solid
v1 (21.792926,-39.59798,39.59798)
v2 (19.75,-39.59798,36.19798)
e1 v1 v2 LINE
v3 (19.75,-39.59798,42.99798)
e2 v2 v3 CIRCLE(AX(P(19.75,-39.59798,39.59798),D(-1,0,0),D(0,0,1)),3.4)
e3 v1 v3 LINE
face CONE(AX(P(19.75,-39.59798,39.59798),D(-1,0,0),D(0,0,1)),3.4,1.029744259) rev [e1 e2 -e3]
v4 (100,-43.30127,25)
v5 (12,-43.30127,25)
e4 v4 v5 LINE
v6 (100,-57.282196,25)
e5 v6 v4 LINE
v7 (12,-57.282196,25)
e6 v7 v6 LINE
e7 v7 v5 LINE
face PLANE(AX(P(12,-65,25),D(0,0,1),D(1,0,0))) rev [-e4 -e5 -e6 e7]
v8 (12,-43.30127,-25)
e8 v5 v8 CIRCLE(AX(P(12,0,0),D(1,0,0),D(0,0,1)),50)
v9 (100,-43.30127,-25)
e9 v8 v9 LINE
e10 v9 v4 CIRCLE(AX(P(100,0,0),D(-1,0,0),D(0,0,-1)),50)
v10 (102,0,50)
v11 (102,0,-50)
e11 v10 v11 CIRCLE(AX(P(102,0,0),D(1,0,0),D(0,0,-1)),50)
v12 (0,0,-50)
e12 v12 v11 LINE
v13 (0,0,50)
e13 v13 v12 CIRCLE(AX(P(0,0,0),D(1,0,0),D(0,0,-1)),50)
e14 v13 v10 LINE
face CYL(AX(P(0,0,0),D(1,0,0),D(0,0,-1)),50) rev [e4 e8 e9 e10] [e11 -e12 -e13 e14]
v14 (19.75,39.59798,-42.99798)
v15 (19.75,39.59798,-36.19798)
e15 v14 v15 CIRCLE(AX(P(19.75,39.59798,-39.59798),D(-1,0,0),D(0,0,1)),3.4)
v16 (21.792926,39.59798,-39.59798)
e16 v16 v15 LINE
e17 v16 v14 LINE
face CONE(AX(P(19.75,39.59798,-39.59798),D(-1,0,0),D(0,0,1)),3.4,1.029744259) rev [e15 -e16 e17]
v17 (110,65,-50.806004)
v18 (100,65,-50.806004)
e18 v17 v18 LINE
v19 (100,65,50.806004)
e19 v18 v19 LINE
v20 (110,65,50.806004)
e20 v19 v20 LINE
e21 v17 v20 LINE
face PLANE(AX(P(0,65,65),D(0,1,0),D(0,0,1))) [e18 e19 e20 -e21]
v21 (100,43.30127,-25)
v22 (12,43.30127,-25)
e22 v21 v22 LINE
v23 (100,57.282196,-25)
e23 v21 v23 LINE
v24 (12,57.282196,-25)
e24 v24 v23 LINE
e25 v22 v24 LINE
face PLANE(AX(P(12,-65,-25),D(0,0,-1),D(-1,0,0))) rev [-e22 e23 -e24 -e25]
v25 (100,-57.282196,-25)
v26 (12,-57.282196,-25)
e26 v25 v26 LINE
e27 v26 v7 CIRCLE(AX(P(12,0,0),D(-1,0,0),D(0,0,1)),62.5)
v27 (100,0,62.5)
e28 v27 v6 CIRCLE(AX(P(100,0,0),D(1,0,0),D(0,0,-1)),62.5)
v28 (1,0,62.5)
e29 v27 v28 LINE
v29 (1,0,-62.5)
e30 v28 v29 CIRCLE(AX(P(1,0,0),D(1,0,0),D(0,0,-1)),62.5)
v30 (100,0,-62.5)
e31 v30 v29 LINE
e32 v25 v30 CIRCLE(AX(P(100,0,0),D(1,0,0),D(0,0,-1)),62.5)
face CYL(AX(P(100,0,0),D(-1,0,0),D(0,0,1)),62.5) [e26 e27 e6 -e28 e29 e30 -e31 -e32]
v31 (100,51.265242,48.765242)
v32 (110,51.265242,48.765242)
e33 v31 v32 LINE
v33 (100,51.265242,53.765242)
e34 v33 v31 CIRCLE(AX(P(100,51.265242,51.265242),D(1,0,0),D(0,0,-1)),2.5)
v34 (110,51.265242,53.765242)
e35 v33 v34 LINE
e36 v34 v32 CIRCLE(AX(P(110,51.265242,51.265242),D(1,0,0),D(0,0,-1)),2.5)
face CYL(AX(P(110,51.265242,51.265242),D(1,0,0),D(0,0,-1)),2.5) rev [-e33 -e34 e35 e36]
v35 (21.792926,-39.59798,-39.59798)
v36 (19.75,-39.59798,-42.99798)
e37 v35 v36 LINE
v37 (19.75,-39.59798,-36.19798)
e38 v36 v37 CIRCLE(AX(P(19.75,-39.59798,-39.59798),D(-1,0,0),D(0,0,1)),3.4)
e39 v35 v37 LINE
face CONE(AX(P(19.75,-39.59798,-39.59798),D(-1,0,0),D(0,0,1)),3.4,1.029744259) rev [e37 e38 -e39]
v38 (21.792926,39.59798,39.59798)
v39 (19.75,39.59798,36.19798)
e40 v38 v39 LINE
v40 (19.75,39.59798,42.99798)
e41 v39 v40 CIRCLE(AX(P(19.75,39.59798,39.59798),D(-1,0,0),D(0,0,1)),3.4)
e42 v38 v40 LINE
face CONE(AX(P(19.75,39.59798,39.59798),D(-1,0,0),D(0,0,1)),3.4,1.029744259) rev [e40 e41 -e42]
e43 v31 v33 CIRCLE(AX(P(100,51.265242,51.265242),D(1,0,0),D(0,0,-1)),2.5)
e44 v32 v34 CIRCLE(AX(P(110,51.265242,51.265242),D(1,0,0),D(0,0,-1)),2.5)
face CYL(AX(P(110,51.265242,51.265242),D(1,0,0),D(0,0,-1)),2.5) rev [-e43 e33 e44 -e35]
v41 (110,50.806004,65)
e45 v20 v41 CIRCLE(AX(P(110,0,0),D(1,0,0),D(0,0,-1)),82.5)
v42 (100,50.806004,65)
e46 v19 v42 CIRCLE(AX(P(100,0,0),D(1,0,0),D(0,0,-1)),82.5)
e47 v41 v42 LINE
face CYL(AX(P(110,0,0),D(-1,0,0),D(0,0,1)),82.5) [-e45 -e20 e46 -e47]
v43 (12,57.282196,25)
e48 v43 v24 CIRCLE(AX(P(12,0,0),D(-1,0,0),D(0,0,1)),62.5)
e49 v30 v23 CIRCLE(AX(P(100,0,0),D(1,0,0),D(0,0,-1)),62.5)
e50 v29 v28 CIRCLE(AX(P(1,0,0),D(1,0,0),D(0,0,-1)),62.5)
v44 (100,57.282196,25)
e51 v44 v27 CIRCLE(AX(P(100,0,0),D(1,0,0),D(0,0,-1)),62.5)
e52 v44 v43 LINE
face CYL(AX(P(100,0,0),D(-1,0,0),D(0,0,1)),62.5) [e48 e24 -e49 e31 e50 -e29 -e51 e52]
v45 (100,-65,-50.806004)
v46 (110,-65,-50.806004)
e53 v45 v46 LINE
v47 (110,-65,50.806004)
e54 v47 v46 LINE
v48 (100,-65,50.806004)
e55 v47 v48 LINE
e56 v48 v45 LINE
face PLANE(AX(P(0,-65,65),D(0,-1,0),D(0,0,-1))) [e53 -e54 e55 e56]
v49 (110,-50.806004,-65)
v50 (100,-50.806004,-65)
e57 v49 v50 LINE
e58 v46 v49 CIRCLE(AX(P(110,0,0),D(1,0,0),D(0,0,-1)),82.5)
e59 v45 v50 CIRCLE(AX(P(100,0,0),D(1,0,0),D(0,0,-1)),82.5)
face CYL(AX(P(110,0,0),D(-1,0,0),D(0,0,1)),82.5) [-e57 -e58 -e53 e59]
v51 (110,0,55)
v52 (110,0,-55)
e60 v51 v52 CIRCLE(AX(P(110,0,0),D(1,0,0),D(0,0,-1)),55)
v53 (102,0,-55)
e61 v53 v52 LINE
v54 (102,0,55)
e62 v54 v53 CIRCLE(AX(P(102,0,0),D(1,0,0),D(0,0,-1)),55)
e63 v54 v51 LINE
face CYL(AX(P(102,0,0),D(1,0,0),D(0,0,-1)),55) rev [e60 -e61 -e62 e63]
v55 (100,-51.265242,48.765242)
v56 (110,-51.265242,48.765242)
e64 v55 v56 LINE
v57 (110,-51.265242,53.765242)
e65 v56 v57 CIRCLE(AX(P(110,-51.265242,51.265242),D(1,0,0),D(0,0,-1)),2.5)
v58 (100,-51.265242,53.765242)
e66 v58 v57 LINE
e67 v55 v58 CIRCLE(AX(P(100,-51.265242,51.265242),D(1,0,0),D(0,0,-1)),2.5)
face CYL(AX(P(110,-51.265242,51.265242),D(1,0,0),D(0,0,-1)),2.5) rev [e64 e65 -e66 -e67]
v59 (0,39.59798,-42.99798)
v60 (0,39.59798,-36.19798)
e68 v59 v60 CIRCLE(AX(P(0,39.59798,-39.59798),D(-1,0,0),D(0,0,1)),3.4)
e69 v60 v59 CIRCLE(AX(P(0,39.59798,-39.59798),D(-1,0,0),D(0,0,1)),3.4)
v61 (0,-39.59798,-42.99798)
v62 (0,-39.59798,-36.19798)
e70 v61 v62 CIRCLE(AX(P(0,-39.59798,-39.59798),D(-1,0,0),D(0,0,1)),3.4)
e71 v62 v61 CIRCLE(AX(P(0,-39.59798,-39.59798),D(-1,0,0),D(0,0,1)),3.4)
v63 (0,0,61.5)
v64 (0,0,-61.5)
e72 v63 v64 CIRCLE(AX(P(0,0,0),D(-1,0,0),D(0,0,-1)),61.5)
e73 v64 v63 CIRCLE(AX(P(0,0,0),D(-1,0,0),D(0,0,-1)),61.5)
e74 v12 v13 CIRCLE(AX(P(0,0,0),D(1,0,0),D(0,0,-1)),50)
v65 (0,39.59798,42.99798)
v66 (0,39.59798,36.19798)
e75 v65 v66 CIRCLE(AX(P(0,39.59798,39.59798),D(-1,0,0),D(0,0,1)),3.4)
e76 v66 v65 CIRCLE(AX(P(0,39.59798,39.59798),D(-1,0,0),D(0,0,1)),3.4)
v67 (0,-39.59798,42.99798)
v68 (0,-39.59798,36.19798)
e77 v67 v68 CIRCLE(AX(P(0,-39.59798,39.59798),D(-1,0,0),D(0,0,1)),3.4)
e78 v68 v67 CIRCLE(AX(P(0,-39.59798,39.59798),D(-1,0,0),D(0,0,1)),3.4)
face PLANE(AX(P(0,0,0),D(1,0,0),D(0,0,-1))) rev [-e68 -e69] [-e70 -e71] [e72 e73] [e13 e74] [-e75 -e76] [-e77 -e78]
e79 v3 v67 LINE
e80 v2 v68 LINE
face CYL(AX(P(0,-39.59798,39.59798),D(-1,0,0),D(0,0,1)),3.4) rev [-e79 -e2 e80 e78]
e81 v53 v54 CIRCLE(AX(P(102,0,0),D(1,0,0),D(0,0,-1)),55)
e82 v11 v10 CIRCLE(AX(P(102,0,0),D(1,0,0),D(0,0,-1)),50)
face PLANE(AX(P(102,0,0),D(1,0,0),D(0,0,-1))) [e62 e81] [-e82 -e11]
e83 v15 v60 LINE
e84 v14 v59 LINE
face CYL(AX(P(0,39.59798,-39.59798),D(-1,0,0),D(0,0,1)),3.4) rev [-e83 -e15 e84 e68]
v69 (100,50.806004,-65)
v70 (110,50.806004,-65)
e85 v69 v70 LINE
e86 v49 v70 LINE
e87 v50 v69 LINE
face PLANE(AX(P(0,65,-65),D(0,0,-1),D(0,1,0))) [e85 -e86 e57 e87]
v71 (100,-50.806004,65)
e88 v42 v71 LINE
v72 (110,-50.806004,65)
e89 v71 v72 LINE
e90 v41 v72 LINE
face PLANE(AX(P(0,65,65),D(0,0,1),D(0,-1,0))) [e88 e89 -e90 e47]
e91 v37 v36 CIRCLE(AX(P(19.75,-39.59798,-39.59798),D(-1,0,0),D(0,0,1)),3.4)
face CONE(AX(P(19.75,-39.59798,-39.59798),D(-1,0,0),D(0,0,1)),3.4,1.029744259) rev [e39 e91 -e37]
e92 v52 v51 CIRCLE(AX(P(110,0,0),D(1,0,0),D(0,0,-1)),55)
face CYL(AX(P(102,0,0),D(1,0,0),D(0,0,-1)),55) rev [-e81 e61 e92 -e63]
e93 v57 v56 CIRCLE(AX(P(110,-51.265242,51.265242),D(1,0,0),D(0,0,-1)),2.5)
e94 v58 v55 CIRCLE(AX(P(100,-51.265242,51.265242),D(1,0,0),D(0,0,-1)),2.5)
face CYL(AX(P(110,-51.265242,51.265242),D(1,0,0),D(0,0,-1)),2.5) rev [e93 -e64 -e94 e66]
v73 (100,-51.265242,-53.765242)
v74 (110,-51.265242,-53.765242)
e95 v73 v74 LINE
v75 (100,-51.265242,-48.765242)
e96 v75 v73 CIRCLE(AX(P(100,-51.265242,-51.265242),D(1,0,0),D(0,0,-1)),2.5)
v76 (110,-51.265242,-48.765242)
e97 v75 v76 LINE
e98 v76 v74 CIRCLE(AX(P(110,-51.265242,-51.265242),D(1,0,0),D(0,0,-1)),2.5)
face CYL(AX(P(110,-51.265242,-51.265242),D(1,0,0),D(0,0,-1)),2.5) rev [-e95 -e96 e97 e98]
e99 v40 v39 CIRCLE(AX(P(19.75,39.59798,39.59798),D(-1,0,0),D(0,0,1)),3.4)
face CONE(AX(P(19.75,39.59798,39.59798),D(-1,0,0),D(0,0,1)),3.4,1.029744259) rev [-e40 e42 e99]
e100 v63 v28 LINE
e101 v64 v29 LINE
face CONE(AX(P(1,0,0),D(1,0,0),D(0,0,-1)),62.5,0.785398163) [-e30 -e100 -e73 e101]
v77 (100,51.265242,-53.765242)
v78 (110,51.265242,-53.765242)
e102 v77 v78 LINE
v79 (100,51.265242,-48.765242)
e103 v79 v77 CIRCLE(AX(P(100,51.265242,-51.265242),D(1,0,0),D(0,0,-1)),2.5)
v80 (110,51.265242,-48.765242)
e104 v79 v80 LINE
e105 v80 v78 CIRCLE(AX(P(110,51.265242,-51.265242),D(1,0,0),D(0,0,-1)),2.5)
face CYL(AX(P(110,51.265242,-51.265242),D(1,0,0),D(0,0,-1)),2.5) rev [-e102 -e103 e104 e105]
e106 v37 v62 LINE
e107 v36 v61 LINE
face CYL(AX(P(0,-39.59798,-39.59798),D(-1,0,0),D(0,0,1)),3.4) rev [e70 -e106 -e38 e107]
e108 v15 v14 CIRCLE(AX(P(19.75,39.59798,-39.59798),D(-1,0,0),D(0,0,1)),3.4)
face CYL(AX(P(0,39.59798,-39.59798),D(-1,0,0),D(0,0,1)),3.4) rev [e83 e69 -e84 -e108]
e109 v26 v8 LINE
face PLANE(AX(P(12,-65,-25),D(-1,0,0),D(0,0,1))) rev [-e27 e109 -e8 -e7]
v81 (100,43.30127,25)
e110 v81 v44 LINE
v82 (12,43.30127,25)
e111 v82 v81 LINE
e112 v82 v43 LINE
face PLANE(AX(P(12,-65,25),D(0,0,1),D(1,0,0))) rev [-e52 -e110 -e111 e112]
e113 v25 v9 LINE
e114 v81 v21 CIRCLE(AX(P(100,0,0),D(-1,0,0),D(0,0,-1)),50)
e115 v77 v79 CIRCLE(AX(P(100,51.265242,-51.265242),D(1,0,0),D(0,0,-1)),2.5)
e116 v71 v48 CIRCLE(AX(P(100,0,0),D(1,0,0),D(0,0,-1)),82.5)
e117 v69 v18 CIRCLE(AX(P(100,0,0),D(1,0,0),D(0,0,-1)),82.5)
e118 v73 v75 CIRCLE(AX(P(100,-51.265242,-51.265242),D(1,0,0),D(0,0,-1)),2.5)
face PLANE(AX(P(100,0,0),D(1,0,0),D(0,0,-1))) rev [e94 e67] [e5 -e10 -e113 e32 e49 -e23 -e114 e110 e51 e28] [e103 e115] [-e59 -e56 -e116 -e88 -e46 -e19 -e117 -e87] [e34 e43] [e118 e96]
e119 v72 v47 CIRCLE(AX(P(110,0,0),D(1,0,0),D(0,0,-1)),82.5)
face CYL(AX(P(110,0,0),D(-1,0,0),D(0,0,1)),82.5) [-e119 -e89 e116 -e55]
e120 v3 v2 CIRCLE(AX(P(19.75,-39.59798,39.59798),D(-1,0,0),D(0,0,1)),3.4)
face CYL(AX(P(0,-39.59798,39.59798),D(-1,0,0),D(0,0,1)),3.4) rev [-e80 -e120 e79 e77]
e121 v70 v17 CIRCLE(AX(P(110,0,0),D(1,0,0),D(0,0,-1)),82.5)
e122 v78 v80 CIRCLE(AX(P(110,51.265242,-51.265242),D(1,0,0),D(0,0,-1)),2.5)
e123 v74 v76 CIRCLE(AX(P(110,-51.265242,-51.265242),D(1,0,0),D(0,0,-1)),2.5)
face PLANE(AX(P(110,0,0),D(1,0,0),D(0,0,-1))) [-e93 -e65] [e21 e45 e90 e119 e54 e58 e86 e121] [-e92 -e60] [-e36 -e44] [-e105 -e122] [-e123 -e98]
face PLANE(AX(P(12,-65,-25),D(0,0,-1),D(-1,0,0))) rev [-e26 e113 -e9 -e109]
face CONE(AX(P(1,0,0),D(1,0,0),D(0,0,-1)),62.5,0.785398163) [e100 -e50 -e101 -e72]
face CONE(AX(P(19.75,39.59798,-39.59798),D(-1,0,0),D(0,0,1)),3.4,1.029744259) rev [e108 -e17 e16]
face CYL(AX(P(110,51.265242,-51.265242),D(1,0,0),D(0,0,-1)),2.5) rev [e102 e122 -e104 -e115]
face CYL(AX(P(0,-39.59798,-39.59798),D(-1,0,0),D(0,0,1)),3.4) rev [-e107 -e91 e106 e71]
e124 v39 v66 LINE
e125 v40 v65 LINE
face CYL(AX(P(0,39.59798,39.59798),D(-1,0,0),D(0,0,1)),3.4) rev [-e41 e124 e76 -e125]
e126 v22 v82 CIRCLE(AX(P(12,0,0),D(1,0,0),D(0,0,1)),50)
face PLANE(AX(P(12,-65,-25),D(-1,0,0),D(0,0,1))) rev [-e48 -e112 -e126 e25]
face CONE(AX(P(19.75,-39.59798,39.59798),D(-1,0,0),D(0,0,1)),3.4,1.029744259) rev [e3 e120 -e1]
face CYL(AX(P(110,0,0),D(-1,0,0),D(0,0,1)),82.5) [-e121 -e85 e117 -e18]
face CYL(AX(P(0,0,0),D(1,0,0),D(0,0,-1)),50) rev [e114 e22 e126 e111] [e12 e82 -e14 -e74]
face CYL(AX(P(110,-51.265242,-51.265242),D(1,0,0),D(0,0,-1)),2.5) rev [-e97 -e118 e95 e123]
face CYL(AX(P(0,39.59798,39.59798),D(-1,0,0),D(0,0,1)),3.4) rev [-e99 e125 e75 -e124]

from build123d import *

# Parameters (mm, degrees)
SKETCH_1_R               = 62.5
EXTRUDE_1_DEPTH          = 100
SKETCH_2_R               = 82.5
EXTRUDE_2_DEPTH          = 10
SKETCH_3_OUTSIDE_W       = 218.594
SKETCH_3_OUTSIDE_H       = 218.594
SKETCH_3_OUTSIDE_W_2     = 130
SKETCH_3_OUTSIDE_H_2     = 130
CUT_EXTRUDE_1_DEPTH      = 161.351177108
SKETCH_4_R               = 55
CUT_EXTRUDE_2_DEPTH      = 8
PATTERN_CIRCULAR_1_COUNT = 4
SKETCH_7_R               = 50
CUT_EXTRUDE_3_DEPTH      = 138.309868546
CUT_EXTRUDE_4_DEPTH      = 144.352711868
CUT_EXTRUDE_4_DEPTH_BACK = 144.352711868
SKETCH_8_W               = 88
SKETCH_8_H               = 50
PATTERN_CIRCULAR_2_COUNT = 4
CHAMFER_1_SIZE           = 1


with BuildPart() as part:
    # 草图1 → 凸台-拉伸1 (new body)
    with BuildSketch(Plane(origin=(0, 0, 0), x_dir=(0, 0, -1), z_dir=(1, 0, 0))):
        Circle(SKETCH_1_R)
    extrude(amount=EXTRUDE_1_DEPTH)

    # 草图2 → 凸台-拉伸2 (add)
    with BuildSketch(Plane(origin=(100, 0, 0), x_dir=(0, 0, -1), z_dir=(1, 0, 0))):
        Circle(SKETCH_2_R)
    extrude(amount=EXTRUDE_2_DEPTH)

    # 草图3 outside → 切除-拉伸1 (cut, through all)
    with BuildSketch(Plane(origin=(110, 0, 0), x_dir=(0, 0, -1), z_dir=(1, 0, 0))):
        Rectangle(SKETCH_3_OUTSIDE_W, SKETCH_3_OUTSIDE_H)
        Rectangle(SKETCH_3_OUTSIDE_W_2, SKETCH_3_OUTSIDE_H_2, mode=Mode.SUBTRACT)
    extrude(amount=-CUT_EXTRUDE_1_DEPTH, mode=Mode.SUBTRACT)

    # 草图4 → 切除-拉伸2 (cut)
    with BuildSketch(Plane(origin=(110, 0, 0), x_dir=(0, 0, -1), z_dir=(1, 0, 0))):
        Circle(SKETCH_4_R)
    extrude(amount=-CUT_EXTRUDE_2_DEPTH, mode=Mode.SUBTRACT)

    # 草图6 → M6 螺纹孔1 (revolve, cut)
    with BuildSketch(Plane(origin=(110, 51.265241636, 51.265241636), x_dir=(0, 0, -1), z_dir=(0, 1, 0))):
        Polygon((0, 0), (0, 16.502151548), (2.5, 15), (2.5, 0), align=None)
    hole_wizard_m6_1 = revolve(axis=Axis((116.35, 51.265241636, 51.265241636), (-1, 0, 0)), mode=Mode.SUBTRACT)

    # 阵列(圆周)1: M6 螺纹孔1 ×4 about axis
    pattern_circular_1_axis = Axis((0, 0, 0), (1, 0, 0))
    for i in range(1, PATTERN_CIRCULAR_1_COUNT):
        add(hole_wizard_m6_1.rotate(pattern_circular_1_axis, i * 360 / PATTERN_CIRCULAR_1_COUNT), mode=Mode.SUBTRACT)

    # 草图7 → 切除-拉伸3 (cut, through all)
    with BuildSketch(Plane(origin=(102, 0, 0), x_dir=(0, 0, -1), z_dir=(1, 0, 0))):
        Circle(SKETCH_7_R)
    extrude(amount=-CUT_EXTRUDE_3_DEPTH, mode=Mode.SUBTRACT)

    # 草图8 → 切除-拉伸4 (cut, two sides: drawn at the far end of the back side and taken through both)
    with BuildSketch(Plane(origin=(0, 0, 0), x_dir=(1, 0, 0), z_dir=(0, 1, 0)).offset(-CUT_EXTRUDE_4_DEPTH_BACK)):
        with Locations((56, 0)):
            Rectangle(SKETCH_8_W, SKETCH_8_H)
    extrude(amount=CUT_EXTRUDE_4_DEPTH + CUT_EXTRUDE_4_DEPTH_BACK, mode=Mode.SUBTRACT)

    # 草图10 → M8 螺纹孔1 (revolve, cut)
    with BuildSketch(Plane(origin=(0, 39.597979746, -39.597979746), x_dir=(0, 0, 1), z_dir=(0, 1, 0))):
        Polygon((0, 0), (0, 21.792926105), (3.4, 19.75), (3.4, 0), align=None)
    hole_wizard_m8_1 = revolve(axis=Axis((-6.35, 39.597979746, -39.597979746), (1, 0, 0)), mode=Mode.SUBTRACT)

    # 阵列(圆周)2: M8 螺纹孔1 ×4 about axis
    pattern_circular_2_axis = Axis((0, 0, 0), (1, 0, 0))
    for i in range(1, PATTERN_CIRCULAR_2_COUNT):
        add(hole_wizard_m8_1.rotate(pattern_circular_2_axis, i * 360 / PATTERN_CIRCULAR_2_COUNT), mode=Mode.SUBTRACT)

    # 倒角1
    chamfer_1_edges = [part.edges().sort_by_distance(p)[0] for p in [
        (0, 0, 62.5),
    ]]
    chamfer(chamfer_1_edges, length=CHAMFER_1_SIZE)


solid = part.part
